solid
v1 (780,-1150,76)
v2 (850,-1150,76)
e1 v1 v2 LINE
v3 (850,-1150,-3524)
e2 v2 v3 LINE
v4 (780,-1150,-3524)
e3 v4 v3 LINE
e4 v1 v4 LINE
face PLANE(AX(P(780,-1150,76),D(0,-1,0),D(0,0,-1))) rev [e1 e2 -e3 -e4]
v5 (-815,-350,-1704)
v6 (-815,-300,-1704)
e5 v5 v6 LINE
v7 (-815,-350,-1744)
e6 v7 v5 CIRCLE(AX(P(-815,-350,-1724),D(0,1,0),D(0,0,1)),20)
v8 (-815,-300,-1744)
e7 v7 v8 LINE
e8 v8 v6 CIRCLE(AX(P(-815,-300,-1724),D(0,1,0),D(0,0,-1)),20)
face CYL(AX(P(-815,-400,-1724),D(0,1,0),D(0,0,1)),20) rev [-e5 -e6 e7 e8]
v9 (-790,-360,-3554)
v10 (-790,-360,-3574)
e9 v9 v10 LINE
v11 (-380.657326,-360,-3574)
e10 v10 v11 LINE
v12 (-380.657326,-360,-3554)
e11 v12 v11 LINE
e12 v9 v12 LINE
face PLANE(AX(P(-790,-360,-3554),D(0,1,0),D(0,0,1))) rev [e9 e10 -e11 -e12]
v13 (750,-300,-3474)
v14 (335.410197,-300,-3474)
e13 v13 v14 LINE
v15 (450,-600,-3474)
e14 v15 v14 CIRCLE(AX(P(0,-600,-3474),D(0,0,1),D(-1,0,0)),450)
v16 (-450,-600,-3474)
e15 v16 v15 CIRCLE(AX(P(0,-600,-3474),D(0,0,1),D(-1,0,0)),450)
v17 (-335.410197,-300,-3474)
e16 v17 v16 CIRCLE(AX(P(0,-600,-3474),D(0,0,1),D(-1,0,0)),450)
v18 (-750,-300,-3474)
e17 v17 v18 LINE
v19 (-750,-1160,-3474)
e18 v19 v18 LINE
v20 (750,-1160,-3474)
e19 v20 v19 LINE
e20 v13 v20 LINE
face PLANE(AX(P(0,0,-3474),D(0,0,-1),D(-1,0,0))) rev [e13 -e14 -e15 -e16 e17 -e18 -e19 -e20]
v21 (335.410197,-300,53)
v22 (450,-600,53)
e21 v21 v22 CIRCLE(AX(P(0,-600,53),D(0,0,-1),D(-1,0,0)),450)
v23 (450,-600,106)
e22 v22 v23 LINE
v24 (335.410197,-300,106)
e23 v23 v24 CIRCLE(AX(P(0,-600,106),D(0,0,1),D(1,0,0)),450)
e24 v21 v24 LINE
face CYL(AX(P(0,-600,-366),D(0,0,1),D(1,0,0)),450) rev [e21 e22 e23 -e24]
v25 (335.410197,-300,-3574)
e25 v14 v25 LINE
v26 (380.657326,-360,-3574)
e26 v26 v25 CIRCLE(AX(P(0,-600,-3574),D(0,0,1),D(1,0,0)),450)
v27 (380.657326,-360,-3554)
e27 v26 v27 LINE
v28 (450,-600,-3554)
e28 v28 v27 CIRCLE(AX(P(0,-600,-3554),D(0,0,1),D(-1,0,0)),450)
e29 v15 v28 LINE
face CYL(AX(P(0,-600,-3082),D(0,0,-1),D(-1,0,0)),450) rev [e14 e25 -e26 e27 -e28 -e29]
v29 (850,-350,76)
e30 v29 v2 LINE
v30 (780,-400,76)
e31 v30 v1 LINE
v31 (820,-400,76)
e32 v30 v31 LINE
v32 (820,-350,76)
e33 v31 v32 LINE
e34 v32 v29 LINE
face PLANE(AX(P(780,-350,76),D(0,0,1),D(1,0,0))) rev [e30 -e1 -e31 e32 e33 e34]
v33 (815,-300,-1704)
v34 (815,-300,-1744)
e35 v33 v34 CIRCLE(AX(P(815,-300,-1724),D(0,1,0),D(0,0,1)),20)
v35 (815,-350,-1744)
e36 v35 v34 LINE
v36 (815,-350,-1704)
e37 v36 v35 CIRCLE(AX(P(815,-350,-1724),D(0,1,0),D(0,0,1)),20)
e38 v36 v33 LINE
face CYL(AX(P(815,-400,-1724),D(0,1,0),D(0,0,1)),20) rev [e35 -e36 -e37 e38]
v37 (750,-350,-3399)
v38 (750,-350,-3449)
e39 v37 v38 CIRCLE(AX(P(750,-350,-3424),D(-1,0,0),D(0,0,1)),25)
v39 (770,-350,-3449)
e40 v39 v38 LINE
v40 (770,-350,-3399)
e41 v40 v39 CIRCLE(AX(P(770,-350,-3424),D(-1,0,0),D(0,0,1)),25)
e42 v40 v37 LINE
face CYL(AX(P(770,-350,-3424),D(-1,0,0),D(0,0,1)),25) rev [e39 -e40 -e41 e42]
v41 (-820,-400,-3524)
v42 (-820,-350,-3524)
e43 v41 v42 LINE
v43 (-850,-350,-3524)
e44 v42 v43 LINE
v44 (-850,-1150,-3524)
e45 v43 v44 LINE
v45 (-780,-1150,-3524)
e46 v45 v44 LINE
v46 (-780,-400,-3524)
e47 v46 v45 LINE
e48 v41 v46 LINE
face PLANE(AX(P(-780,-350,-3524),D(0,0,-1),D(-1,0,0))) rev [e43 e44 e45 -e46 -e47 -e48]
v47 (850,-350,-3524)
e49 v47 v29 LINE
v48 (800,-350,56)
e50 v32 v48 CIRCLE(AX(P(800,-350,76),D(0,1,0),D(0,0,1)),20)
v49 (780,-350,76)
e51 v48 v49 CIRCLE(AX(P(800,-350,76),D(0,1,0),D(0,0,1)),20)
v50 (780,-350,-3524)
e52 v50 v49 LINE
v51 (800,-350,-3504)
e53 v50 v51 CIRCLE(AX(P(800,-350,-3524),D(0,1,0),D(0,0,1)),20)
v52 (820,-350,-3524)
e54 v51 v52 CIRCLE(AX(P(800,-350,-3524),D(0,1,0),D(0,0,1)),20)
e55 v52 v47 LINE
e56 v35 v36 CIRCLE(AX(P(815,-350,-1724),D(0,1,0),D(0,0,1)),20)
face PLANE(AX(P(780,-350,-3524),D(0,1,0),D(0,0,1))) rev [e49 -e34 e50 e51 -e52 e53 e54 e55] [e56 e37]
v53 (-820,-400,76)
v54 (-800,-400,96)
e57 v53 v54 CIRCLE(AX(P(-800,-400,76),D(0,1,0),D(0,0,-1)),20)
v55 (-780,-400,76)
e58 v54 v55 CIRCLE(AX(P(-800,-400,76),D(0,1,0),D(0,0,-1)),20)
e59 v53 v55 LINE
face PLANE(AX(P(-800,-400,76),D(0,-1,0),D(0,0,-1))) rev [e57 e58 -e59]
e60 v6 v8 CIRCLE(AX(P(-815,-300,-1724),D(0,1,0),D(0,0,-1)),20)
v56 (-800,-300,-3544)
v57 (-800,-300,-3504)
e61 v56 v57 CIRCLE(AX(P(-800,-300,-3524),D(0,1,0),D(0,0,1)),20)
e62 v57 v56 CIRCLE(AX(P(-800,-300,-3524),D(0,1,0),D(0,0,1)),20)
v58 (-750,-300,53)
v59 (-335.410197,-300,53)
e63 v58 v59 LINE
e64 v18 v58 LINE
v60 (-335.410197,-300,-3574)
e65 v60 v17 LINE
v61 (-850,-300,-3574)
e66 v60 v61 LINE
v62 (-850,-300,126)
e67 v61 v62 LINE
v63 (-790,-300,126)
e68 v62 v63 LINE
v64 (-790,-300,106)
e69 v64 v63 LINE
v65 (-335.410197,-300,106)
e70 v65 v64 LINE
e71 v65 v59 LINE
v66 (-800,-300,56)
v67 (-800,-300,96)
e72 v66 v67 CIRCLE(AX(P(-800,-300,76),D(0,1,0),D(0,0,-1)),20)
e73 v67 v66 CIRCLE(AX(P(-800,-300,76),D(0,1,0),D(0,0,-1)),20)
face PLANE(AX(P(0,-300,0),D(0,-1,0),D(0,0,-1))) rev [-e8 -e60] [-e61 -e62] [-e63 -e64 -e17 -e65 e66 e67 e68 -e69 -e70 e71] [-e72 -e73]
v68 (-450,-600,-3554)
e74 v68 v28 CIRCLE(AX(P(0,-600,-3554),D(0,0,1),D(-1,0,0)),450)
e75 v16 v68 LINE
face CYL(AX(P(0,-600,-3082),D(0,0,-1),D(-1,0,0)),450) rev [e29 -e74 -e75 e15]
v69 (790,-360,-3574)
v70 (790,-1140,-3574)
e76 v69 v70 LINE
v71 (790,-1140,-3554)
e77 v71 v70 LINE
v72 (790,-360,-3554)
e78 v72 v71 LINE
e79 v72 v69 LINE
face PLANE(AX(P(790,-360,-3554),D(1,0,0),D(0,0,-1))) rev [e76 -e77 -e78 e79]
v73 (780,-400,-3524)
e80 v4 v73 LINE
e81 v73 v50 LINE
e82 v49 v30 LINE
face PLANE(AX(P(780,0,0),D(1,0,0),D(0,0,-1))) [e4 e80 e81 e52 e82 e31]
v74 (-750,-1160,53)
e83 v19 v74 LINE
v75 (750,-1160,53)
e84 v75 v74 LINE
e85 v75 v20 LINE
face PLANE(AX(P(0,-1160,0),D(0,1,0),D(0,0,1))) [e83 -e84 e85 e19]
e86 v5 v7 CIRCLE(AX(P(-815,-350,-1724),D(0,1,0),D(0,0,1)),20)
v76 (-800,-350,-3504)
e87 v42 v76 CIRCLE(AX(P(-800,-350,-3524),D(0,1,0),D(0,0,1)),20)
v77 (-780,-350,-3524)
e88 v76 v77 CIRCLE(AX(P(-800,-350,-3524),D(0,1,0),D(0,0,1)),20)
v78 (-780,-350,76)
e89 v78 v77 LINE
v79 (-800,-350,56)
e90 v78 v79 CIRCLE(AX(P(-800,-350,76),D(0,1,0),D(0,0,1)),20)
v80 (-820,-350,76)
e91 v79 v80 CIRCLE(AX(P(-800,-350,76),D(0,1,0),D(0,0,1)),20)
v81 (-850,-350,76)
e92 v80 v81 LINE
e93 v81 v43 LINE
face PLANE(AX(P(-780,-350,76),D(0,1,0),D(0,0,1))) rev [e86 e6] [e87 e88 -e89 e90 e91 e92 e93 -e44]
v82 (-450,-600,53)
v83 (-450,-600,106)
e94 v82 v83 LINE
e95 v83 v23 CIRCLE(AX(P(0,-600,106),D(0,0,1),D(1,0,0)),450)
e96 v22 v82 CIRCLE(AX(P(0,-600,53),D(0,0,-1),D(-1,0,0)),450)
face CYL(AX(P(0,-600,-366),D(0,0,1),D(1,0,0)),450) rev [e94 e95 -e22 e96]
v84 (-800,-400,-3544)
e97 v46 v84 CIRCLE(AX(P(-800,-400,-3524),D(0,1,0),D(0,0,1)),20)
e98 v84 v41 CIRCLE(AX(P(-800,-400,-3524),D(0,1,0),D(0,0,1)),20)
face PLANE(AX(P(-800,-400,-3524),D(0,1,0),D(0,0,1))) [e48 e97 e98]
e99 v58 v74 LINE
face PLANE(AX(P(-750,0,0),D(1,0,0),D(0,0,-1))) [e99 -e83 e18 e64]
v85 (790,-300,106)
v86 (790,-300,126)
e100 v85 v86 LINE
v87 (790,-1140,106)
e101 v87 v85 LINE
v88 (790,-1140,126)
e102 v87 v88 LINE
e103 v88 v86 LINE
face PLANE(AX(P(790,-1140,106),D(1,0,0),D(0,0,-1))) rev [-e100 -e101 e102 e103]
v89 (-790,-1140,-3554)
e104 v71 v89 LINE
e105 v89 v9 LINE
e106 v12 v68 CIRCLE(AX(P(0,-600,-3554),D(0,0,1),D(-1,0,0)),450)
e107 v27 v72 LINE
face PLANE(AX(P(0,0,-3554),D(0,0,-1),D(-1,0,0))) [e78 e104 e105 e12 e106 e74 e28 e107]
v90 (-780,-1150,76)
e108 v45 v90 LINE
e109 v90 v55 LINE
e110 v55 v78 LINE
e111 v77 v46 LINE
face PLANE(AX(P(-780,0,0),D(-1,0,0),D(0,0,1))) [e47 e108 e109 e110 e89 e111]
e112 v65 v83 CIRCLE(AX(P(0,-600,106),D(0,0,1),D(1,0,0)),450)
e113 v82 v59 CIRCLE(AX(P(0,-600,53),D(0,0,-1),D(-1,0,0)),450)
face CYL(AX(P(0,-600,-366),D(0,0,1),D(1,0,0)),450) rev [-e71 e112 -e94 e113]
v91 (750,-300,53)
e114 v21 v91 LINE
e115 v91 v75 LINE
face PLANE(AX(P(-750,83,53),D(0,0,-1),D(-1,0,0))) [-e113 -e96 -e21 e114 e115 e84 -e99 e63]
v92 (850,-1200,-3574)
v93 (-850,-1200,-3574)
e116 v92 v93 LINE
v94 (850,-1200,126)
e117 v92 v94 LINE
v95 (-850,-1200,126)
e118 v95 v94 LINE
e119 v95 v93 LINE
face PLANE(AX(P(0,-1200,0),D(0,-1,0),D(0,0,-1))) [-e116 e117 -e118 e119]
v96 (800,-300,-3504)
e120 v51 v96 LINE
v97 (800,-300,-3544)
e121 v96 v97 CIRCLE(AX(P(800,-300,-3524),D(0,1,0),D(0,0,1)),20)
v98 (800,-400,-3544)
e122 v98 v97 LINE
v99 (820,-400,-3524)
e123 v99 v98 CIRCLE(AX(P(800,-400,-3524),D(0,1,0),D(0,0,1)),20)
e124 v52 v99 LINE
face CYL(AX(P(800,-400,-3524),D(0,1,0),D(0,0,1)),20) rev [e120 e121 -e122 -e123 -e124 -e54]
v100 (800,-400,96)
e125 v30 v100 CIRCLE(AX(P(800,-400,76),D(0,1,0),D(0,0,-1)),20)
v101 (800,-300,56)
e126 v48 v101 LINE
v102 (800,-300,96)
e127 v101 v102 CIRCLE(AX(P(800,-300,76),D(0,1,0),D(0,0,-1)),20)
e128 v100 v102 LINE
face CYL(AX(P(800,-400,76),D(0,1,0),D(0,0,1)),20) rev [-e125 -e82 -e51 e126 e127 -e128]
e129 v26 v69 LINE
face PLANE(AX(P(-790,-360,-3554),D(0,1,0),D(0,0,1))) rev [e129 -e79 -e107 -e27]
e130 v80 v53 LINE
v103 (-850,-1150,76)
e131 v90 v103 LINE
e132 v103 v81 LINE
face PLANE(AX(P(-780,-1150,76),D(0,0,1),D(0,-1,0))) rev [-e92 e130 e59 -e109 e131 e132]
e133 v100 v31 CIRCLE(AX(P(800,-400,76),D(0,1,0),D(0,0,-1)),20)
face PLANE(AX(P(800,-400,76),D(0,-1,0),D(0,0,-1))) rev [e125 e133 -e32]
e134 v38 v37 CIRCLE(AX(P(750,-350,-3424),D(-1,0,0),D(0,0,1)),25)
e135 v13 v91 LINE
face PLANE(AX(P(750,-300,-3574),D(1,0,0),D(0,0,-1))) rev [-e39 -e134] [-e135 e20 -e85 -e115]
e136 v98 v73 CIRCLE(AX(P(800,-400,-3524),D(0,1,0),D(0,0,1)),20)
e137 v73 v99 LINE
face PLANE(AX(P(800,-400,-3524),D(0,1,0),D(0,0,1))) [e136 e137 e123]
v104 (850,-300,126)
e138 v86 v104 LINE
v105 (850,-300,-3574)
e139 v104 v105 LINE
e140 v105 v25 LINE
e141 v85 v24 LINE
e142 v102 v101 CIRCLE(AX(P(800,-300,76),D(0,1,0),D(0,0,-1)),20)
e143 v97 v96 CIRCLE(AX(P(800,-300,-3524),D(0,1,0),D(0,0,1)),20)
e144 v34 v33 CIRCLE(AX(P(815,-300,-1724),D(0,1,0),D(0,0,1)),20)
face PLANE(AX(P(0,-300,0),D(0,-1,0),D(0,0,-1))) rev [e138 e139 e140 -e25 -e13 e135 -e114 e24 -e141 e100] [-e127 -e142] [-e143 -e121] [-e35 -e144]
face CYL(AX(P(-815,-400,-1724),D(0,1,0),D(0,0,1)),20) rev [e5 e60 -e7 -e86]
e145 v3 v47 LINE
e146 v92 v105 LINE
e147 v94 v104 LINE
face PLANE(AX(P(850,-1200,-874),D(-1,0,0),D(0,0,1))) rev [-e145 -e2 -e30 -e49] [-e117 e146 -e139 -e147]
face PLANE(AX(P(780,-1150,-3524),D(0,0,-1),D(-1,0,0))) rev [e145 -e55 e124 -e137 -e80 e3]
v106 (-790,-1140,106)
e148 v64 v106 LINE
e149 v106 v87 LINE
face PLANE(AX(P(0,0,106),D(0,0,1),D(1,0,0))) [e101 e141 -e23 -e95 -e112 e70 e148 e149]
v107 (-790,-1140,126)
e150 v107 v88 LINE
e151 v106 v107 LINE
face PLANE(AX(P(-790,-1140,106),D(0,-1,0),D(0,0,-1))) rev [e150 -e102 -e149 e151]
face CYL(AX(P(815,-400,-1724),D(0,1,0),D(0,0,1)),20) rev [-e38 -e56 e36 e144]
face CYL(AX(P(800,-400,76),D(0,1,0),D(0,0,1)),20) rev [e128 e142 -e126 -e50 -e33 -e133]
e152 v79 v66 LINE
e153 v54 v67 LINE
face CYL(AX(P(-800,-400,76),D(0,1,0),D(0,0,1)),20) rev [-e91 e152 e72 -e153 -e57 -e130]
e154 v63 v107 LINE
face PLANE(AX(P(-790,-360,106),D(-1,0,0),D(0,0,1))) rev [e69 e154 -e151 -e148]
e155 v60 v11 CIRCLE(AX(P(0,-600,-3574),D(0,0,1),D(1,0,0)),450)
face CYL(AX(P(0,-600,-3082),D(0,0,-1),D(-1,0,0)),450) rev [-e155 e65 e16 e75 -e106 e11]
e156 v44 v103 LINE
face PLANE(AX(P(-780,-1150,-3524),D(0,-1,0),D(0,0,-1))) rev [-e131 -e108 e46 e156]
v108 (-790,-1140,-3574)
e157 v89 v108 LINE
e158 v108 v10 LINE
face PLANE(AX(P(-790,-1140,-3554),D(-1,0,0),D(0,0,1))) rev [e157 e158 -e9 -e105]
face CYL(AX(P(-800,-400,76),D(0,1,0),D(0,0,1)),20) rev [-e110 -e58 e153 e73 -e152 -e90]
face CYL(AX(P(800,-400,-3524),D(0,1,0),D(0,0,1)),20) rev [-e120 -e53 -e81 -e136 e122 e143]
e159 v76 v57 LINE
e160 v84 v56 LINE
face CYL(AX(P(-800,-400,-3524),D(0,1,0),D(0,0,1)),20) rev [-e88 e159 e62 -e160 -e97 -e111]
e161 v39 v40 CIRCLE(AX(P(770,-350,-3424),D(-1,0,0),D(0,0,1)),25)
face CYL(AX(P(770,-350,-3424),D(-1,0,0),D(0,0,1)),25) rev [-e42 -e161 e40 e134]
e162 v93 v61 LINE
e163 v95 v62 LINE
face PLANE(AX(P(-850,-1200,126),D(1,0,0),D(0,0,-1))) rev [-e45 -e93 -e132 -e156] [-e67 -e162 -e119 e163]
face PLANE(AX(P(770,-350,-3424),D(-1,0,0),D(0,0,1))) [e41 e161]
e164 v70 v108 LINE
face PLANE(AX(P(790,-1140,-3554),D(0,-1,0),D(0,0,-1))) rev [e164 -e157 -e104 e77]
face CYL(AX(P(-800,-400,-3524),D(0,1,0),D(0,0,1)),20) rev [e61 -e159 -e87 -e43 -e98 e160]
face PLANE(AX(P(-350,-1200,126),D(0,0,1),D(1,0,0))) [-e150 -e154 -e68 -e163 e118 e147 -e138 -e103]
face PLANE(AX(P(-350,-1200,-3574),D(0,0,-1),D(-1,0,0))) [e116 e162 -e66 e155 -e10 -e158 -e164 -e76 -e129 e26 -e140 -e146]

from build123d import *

# Parameters (mm, degrees)
SKETCH_1_R           = 50
SKETCH_1_R_2         = 42.55
EXTRUDE_1_DEPTH      = 50
SKETCH_3_R           = 45
SKETCH_3_R_2         = 37.55
EXTRUDE_2_DEPTH      = 50
EXTRUDE_START        = -50
EXTRUDE_3_DEPTH      = 50
SKETCH_8_R           = 37.55
EXTRUDE_4_DEPTH      = 50
SKETCH_4_W           = 700
SKETCH_4_H           = 3700
EXTRUDE_5_DEPTH      = 300
SKETCH_12_W          = 500
SKETCH_12_H          = 1000
EXTRUDE_6_DEPTH      = 300
SKETCH_16_W          = 500
SKETCH_16_H          = 2700
EXTRUDE_8_DEPTH      = 300
SKETCH_17_W          = 100
SKETCH_17_H          = 100
EXTRUDE_9_DEPTH      = 600
SKETCH_18_W          = 100
SKETCH_18_H          = 100
EXTRUDE_10_DEPTH     = 600
SKETCH_19_W          = 100
SKETCH_19_H          = 100
EXTRUDE_11_DEPTH     = 3500
SKETCH_20_R          = 25
CUT_EXTRUDE_5_DEPTH  = 20
SKETCH_21_R          = 52.5
SKETCH_21_R_2        = 42.55
EXTRUDE_12_DEPTH     = 50
CUT_EXTRUDE_START    = -356
CUT_EXTRUDE_6_DEPTH  = 356
SKETCH_23_W          = 47.45
SKETCH_23_H          = 50
EXTRUDE_13_DEPTH     = 20
CUT_EXTRUDE_8_DEPTH  = 611
SKETCH_26_W          = 52.45
SKETCH_26_H          = 50
EXTRUDE_14_DEPTH     = 20
SKETCH_27_R          = 6
CUT_EXTRUDE_9_DEPTH  = 20
SKETCH_28_R          = 6
CUT_EXTRUDE_10_DEPTH = 20
EXTRUDE_START_2      = -53
EXTRUDE_15_DEPTH     = 53
EXTRUDE_START_3      = 3
EXTRUDE_16_DEPTH     = 3
EXTRUDE_17_DEPTH     = 3
EXTRUDE_18_DEPTH     = 53
SKETCH_31_W          = 3500
SKETCH_31_H          = 500
EXTRUDE_19_DEPTH     = 100
SKETCH_33_W          = 500
SKETCH_33_H          = 3700
EXTRUDE_20_DEPTH     = 300
EXTRUDE_21_DEPTH     = 100
SKETCH_35_W          = 1500
SKETCH_35_H          = 600
EXTRUDE_22_DEPTH     = 100
SKETCH_36_W          = 1500
SKETCH_36_H          = 600
EXTRUDE_23_DEPTH     = 100
SKETCH_37_W          = 3600
SKETCH_37_H          = 800
CUT_EXTRUDE_11_DEPTH = 70
SKETCH_38_W          = 1580
SKETCH_38_H          = 780
CUT_EXTRUDE_15_DEPTH = 20
SKETCH_39_W          = 3600
SKETCH_39_H          = 800
CUT_EXTRUDE_16_DEPTH = 70
SKETCH_40_W          = 1580
SKETCH_40_H          = 780
CUT_EXTRUDE_17_DEPTH = 20
SKETCH_43_R          = 20
CUT_EXTRUDE_20_DEPTH = 100
CUT_EXTRUDE_22_DEPTH = 260
SKETCH_44_W          = 1500
SKETCH_44_H          = 3527
CUT_EXTRUDE_24_DEPTH = 983
CUT_EXTRUDE_25_DEPTH = 260
SKETCH_49_W          = 1580
SKETCH_49_H          = 840
CUT_EXTRUDE_26_DEPTH = 20
SKETCH_52_R          = 450
CUT_EXTRUDE_30_DEPTH = 492
SKETCH_53_R          = 450
CUT_EXTRUDE_31_DEPTH = 492


with BuildPart() as part:
    # 草图1 → 凸台-拉伸1 (new body)
    with BuildSketch(Plane.XY):
        Circle(SKETCH_1_R)
        Circle(SKETCH_1_R_2, mode=Mode.SUBTRACT)
    extrude(amount=EXTRUDE_1_DEPTH)

    # 草图7 → 凸台-拉伸3 (add)
    with BuildSketch(Plane.XY.offset(50).offset(EXTRUDE_START)):
        with BuildLine():
            ThreePointArc((50, 0), (0, -50), (-50, 0))
            Line((-50, 0), (-250, -900))
            Line((-250, -900), (250, -900))
            Line((250, -900), (50, 0))
        make_face()
    extrude(amount=EXTRUDE_3_DEPTH)



with BuildPart() as body_2:
    # 草图3 → 凸台-拉伸2 (new body)
    with BuildSketch(Plane(origin=(0, 0, -3374), x_dir=(-1, 0, 0), z_dir=(0, 0, -1))):
        Circle(SKETCH_3_R)
        Circle(SKETCH_3_R_2, mode=Mode.SUBTRACT)
    extrude(amount=EXTRUDE_2_DEPTH)

    # 草图8 → 凸台-拉伸4 (add)
    with BuildSketch(Plane(origin=(0, 0, -3424), x_dir=(-1, 0, 0), z_dir=(0, 0, -1))):
        with BuildLine():
            Line((-43.888190419, 9.941164005), (-250, -900))
            Line((-250, -900), (250, -900))
            Line((250, -900), (43.888190419, 9.941164005))
            ThreePointArc((43.888190419, 9.941164005), (0, 45), (-43.888190419, 9.941164005))
        make_face()
        Circle(SKETCH_8_R, mode=Mode.SUBTRACT)
    extrude(amount=-EXTRUDE_4_DEPTH)


with BuildPart() as part_1:
    add(part.part)

    add(body_2.part)  # 凸台-拉伸5 merges body 2
    # 草图4 → 凸台-拉伸5 (add)
    with BuildSketch(Plane(origin=(0, -900, 0), x_dir=(1, 0, 0), z_dir=(0, 1, 0))):
        with Locations((0, 1724)):
            Rectangle(SKETCH_4_W, SKETCH_4_H)
    extrude(amount=-EXTRUDE_5_DEPTH)

    # 草图12 → 凸台-拉伸6 (add)
    with BuildSketch(Plane(origin=(0, -900, 0), x_dir=(1, 0, 0), z_dir=(0, 1, 0))):
        with Locations((600, 374)):
            Rectangle(SKETCH_12_W, SKETCH_12_H)
    extrude(amount=-EXTRUDE_6_DEPTH)

    # 草图16 → 凸台-拉伸8 (add)
    with BuildSketch(Plane(origin=(0, -900, 0), x_dir=(1, 0, 0), z_dir=(0, 1, 0))):
        with Locations((600, 2224)):
            Rectangle(SKETCH_16_W, SKETCH_16_H)
    extrude(amount=-EXTRUDE_8_DEPTH)

    # 草图17 → 凸台-拉伸9 (add)
    with BuildSketch(Plane(origin=(0, -900, 0), x_dir=(1, 0, 0), z_dir=(0, 1, 0))):
        with Locations((800, 3524)):
            Rectangle(SKETCH_17_W, SKETCH_17_H)
    extrude(amount=EXTRUDE_9_DEPTH)

    # 草图18 → 凸台-拉伸10 (add)
    with BuildSketch(Plane(origin=(0, -900, 0), x_dir=(1, 0, 0), z_dir=(0, 1, 0))):
        with Locations((800, -76)):
            Rectangle(SKETCH_18_W, SKETCH_18_H)
    extrude(amount=EXTRUDE_10_DEPTH)

    # 草图19 → 凸台-拉伸11 (add)
    with BuildSketch(Plane.XY.offset(-3474)):
        with Locations((800, -350)):
            Rectangle(SKETCH_19_W, SKETCH_19_H)
    extrude(amount=EXTRUDE_11_DEPTH)

    # 草图20 → 切除-拉伸5 (cut)
    with BuildSketch(Plane.ZY.offset(-750)):
        with Locations((-3424, -350)):
            Circle(SKETCH_20_R)
    extrude(amount=-CUT_EXTRUDE_5_DEPTH, mode=Mode.SUBTRACT)

    # 草图21 → 凸台-拉伸12 (add)
    with BuildSketch(Plane.XY.offset(50).offset(EXTRUDE_START)):
        Circle(SKETCH_21_R)
        Circle(SKETCH_21_R_2, mode=Mode.SUBTRACT)
    extrude(amount=EXTRUDE_12_DEPTH)

    # 草图22 → 切除-拉伸6 (cut)
    with BuildSketch(Plane.XY.offset(50).offset(CUT_EXTRUDE_START)):
        with BuildLine():
            Line((-52.5, 0), (52.5, 0))
            ThreePointArc((52.5, 0), (0, 52.5), (-52.5, 0))
        make_face()
    extrude(amount=CUT_EXTRUDE_6_DEPTH, mode=Mode.SUBTRACT)

    # 草图23 → 凸台-拉伸13 (add)
    with BuildSketch(Plane(origin=(0, 0, 0), x_dir=(1, 0, 0), z_dir=(0, 1, 0))):
        with Locations((-66.275, -25)):
            Rectangle(SKETCH_23_W, SKETCH_23_H)
        with Locations((66.275, -25)):
            Rectangle(SKETCH_23_W, SKETCH_23_H)
    extrude(amount=-EXTRUDE_13_DEPTH)

    # 草图24 → 切除-拉伸8 (cut)
    with BuildSketch(Plane(origin=(0, 0, -3424), x_dir=(-1, 0, 0), z_dir=(0, 0, -1))):
        with BuildLine():
            Line((-55, 0), (55, 0))
            ThreePointArc((55, 0), (0, 55), (-55, 0))
        make_face()
    extrude(amount=-CUT_EXTRUDE_8_DEPTH, mode=Mode.SUBTRACT)

    # 草图26 → 凸台-拉伸14 (add)
    with BuildSketch(Plane(origin=(0, 0, 0), x_dir=(1, 0, 0), z_dir=(0, 1, 0))):
        with Locations((-63.775, 3399)):
            Rectangle(SKETCH_26_W, SKETCH_26_H)
        with Locations((63.775, 3399)):
            Rectangle(SKETCH_26_W, SKETCH_26_H)
    extrude(amount=-EXTRUDE_14_DEPTH)

    # 草图27 → 切除-拉伸9 (cut)
    with BuildSketch(Plane(origin=(0, 0, 0), x_dir=(1, 0, 0), z_dir=(0, 1, 0))):
        with Locations(Location((-75, -12.5, 0), (0, 0, 270))):
            Circle(SKETCH_27_R)
        with Locations(Location((-75, -37.5, 0), (0, 0, 270))):
            Circle(SKETCH_27_R)
        with Locations(Location((75, -37.5, 0), (0, 0, 90))):
            Circle(SKETCH_27_R)
        with Locations(Location((75, -12.5, 0), (0, 0, 90))):
            Circle(SKETCH_27_R)
    extrude(amount=-CUT_EXTRUDE_9_DEPTH, mode=Mode.SUBTRACT)

    # 草图28 → 切除-拉伸10 (cut)
    with BuildSketch(Plane(origin=(0, 0, 0), x_dir=(1, 0, 0), z_dir=(0, 1, 0))):
        with Locations(Location((-75, 3411.5, 0), (0, 0, 270))):
            Circle(SKETCH_28_R)
        with Locations(Location((-75, 3386.5, 0), (0, 0, 270))):
            Circle(SKETCH_28_R)
        with Locations(Location((75, 3386.5, 0), (0, 0, 90))):
            Circle(SKETCH_28_R)
        with Locations(Location((75, 3411.5, 0), (0, 0, 90))):
            Circle(SKETCH_28_R)
    extrude(amount=-CUT_EXTRUDE_10_DEPTH, mode=Mode.SUBTRACT)

    # 草图29 → 凸台-拉伸15 (add)
    with BuildSketch(Plane.XY.offset(50).offset(EXTRUDE_START_2)):
        with BuildLine():
            Line((-52.5, 0), (-42.55, 0))
            ThreePointArc((-42.55, 0), (0, -42.55), (42.55, 0))
            Line((42.55, 0), (52.5, 0))
            ThreePointArc((52.5, 0), (0, -52.5), (-52.5, 0))
        make_face()
    extrude(amount=EXTRUDE_15_DEPTH)

    # 草图30 → 凸台-拉伸16 (add)
    with BuildSketch(Plane.XY.offset(-3374).offset(EXTRUDE_START_3)):
        with BuildLine():
            Line((-45, 0), (-37.55, 0))
            ThreePointArc((-37.55, 0), (0, -37.55), (37.55, 0))
            Line((37.55, 0), (45, 0))
            ThreePointArc((45, 0), (0, -45), (-45, 0))
        make_face()
    extrude(amount=-EXTRUDE_16_DEPTH)

    # 草图29<2> → 凸台-拉伸17 (add)
    with BuildSketch(Plane.XY.offset(50)):
        with BuildLine():
            Line((-52.5, 0), (-42.55, 0))
            ThreePointArc((-42.55, 0), (0, -42.55), (42.55, 0))
            Line((42.55, 0), (52.5, 0))
            ThreePointArc((52.5, 0), (0, -52.5), (-52.5, 0))
        make_face()
    extrude(amount=EXTRUDE_17_DEPTH)

    # 草图30<2> → 凸台-拉伸18 (add)
    with BuildSketch(Plane.XY.offset(-3374)):
        with BuildLine():
            Line((-45, 0), (-37.55, 0))
            ThreePointArc((-37.55, 0), (0, -37.55), (37.55, 0))
            Line((37.55, 0), (45, 0))
            ThreePointArc((45, 0), (0, -45), (-45, 0))
        make_face()
    extrude(amount=-EXTRUDE_18_DEPTH)

    # 草图31 → 凸台-拉伸19 (add)
    with BuildSketch(Plane.ZY.offset(-750)):
        with Locations((-1724, -650)):
            Rectangle(SKETCH_31_W, SKETCH_31_H)
    extrude(amount=-EXTRUDE_19_DEPTH)

    # 草图33 → 凸台-拉伸20 (add)
    with BuildSketch(Plane(origin=(0, -900, 0), x_dir=(1, 0, 0), z_dir=(0, 1, 0))):
        with Locations((-600, 1724)):
            Rectangle(SKETCH_33_W, SKETCH_33_H)
    extrude(amount=-EXTRUDE_20_DEPTH)

    # 草图34 → 凸台-拉伸21 (add)
    with BuildSketch(Plane.ZY.offset(850)):
        Polygon((126, -300), (126, -900), (126, -1200), (-3574, -1200), (-3574, -900), (-3574, -300), align=None)
    extrude(amount=-EXTRUDE_21_DEPTH)

    # 草图35 → 凸台-拉伸22 (add)
    with BuildSketch(Plane(origin=(0, 0, -3574), x_dir=(-1, 0, 0), z_dir=(0, 0, -1))):
        with Locations((0, -600)):
            Rectangle(SKETCH_35_W, SKETCH_35_H)
    extrude(amount=-EXTRUDE_22_DEPTH)

    # 草图36 → 凸台-拉伸23 (add)
    with BuildSketch(Plane.XY.offset(126)):
        with Locations((0, -600)):
            Rectangle(SKETCH_36_W, SKETCH_36_H)
    extrude(amount=-EXTRUDE_23_DEPTH)

    # 草图37 → 切除-拉伸11 (cut)
    with BuildSketch(Plane.ZY.offset(850)):
        with Locations((-1724, -750)):
            Rectangle(SKETCH_37_W, SKETCH_37_H)
    extrude(amount=-CUT_EXTRUDE_11_DEPTH, mode=Mode.SUBTRACT)

    # 草图38 → 切除-拉伸15 (cut)
    with BuildSketch(Plane(origin=(0, 0, -3574), x_dir=(-1, 0, 0), z_dir=(0, 0, -1))):
        with Locations((0, -750)):
            Rectangle(SKETCH_38_W, SKETCH_38_H)
    extrude(amount=-CUT_EXTRUDE_15_DEPTH, mode=Mode.SUBTRACT)

    # 草图39 → 切除-拉伸16 (cut)
    with BuildSketch(Plane(origin=(850, 0, 0), x_dir=(0, 0, -1), z_dir=(1, 0, 0))):
        with Locations((1724, -750)):
            Rectangle(SKETCH_39_W, SKETCH_39_H)
    extrude(amount=-CUT_EXTRUDE_16_DEPTH, mode=Mode.SUBTRACT)

    # 草图40 → 切除-拉伸17 (cut)
    with BuildSketch(Plane.XY.offset(126)):
        with Locations((0, -750)):
            Rectangle(SKETCH_40_W, SKETCH_40_H)
    extrude(amount=-CUT_EXTRUDE_17_DEPTH, mode=Mode.SUBTRACT)

    # 草图43 → 切除-拉伸20 (cut)
    with BuildSketch(Plane(origin=(0, -300, 0), x_dir=(1, 0, 0), z_dir=(0, 1, 0))):
        with Locations(Location((800, 3524, 0), (0, 0, 270))):
            Circle(SKETCH_43_R)
        with Locations(Location((-800, 3524, 0), (0, 0, 270))):
            Circle(SKETCH_43_R)
        with Locations(Location((815, 1724, 0), (0, 0, 270))):
            Circle(SKETCH_43_R)
        with Locations(Location((-815, 1724, 0), (0, 0, 270))):
            Circle(SKETCH_43_R)
        with Locations(Location((800, -76, 0), (0, 0, 180))):
            Circle(SKETCH_43_R)
        with Locations((-800, -76)):
            Circle(SKETCH_43_R)
    extrude(amount=-CUT_EXTRUDE_20_DEPTH, mode=Mode.SUBTRACT)

    # 草图45 → 切除-拉伸22 (cut)
    with BuildSketch(Plane(origin=(0, -900, 0), x_dir=(1, 0, 0), z_dir=(0, 1, 0))):
        Polygon((-750, 3474), (-750, -26), (-250, -26), (-250, 0), (250, 0), (250, -26), (750, -26), (750, 3474), align=None)
    extrude(amount=-CUT_EXTRUDE_22_DEPTH, mode=Mode.SUBTRACT)


with BuildPart() as cut_extrude_22_piece_1:
    # of the separate pieces the step leaves, piece 1, a body of its own (cut_extrude_22_pieces)
    add(part_1.part.solids().sort_by_distance((850, -1200, 126))[0])


with BuildPart() as cut_extrude_22_piece_2:
    # of the separate pieces the step leaves, piece 2, a body of its own (cut_extrude_22_pieces)
    add(part_1.part.solids().sort_by_distance((-250, -900, -3424))[0])


with BuildPart() as cut_extrude_24_tool:
    # 草图44 → 切除-拉伸24 (new body)
    with BuildSketch(Plane(origin=(0, -900, 0), x_dir=(1, 0, 0), z_dir=(0, 1, 0))):
        with Locations((0, 1710.5)):
            Rectangle(SKETCH_44_W, SKETCH_44_H)
    extrude(amount=CUT_EXTRUDE_24_DEPTH)


with BuildPart() as cut_extrude_22_piece_1_1:
    add(cut_extrude_22_piece_1.part)

    # 切除-拉伸24: cut by cut_extrude_24_tool
    add(cut_extrude_24_tool.part, mode=Mode.SUBTRACT)

    # 草图48 → 切除-拉伸25 (cut)
    with BuildSketch(Plane(origin=(0, -900, 0), x_dir=(1, 0, 0), z_dir=(0, 1, 0))):
        Polygon((250, -26), (250, 0), (-250, 0), (-250, -26), (-750, -26), (-750, -53), (750, -53), (750, -26), align=None)
    extrude(amount=-CUT_EXTRUDE_25_DEPTH, mode=Mode.SUBTRACT)

    # 草图49 → 切除-拉伸26 (cut)
    with BuildSketch(Plane.XY.offset(126)):
        with Locations((0, -720)):
            Rectangle(SKETCH_49_W, SKETCH_49_H)
    extrude(amount=-CUT_EXTRUDE_26_DEPTH, mode=Mode.SUBTRACT)

    # 草图52 → 切除-拉伸30 (cut)
    with BuildSketch(Plane.XY.offset(-3574)):
        with Locations((0, -600)):
            Circle(SKETCH_52_R)
    extrude(amount=CUT_EXTRUDE_30_DEPTH, mode=Mode.SUBTRACT)

    # 草图53 → 切除-拉伸31 (cut)
    with BuildSketch(Plane.XY.offset(126)):
        with Locations((0, -600)):
            Circle(SKETCH_53_R)
    extrude(amount=-CUT_EXTRUDE_31_DEPTH, mode=Mode.SUBTRACT)


with BuildPart() as cut_extrude_22_piece_2_1:
    add(cut_extrude_22_piece_2.part)

    # 切除-拉伸24: cut by cut_extrude_24_tool
    add(cut_extrude_24_tool.part, mode=Mode.SUBTRACT)


solid = cut_extrude_22_piece_1_1.part
